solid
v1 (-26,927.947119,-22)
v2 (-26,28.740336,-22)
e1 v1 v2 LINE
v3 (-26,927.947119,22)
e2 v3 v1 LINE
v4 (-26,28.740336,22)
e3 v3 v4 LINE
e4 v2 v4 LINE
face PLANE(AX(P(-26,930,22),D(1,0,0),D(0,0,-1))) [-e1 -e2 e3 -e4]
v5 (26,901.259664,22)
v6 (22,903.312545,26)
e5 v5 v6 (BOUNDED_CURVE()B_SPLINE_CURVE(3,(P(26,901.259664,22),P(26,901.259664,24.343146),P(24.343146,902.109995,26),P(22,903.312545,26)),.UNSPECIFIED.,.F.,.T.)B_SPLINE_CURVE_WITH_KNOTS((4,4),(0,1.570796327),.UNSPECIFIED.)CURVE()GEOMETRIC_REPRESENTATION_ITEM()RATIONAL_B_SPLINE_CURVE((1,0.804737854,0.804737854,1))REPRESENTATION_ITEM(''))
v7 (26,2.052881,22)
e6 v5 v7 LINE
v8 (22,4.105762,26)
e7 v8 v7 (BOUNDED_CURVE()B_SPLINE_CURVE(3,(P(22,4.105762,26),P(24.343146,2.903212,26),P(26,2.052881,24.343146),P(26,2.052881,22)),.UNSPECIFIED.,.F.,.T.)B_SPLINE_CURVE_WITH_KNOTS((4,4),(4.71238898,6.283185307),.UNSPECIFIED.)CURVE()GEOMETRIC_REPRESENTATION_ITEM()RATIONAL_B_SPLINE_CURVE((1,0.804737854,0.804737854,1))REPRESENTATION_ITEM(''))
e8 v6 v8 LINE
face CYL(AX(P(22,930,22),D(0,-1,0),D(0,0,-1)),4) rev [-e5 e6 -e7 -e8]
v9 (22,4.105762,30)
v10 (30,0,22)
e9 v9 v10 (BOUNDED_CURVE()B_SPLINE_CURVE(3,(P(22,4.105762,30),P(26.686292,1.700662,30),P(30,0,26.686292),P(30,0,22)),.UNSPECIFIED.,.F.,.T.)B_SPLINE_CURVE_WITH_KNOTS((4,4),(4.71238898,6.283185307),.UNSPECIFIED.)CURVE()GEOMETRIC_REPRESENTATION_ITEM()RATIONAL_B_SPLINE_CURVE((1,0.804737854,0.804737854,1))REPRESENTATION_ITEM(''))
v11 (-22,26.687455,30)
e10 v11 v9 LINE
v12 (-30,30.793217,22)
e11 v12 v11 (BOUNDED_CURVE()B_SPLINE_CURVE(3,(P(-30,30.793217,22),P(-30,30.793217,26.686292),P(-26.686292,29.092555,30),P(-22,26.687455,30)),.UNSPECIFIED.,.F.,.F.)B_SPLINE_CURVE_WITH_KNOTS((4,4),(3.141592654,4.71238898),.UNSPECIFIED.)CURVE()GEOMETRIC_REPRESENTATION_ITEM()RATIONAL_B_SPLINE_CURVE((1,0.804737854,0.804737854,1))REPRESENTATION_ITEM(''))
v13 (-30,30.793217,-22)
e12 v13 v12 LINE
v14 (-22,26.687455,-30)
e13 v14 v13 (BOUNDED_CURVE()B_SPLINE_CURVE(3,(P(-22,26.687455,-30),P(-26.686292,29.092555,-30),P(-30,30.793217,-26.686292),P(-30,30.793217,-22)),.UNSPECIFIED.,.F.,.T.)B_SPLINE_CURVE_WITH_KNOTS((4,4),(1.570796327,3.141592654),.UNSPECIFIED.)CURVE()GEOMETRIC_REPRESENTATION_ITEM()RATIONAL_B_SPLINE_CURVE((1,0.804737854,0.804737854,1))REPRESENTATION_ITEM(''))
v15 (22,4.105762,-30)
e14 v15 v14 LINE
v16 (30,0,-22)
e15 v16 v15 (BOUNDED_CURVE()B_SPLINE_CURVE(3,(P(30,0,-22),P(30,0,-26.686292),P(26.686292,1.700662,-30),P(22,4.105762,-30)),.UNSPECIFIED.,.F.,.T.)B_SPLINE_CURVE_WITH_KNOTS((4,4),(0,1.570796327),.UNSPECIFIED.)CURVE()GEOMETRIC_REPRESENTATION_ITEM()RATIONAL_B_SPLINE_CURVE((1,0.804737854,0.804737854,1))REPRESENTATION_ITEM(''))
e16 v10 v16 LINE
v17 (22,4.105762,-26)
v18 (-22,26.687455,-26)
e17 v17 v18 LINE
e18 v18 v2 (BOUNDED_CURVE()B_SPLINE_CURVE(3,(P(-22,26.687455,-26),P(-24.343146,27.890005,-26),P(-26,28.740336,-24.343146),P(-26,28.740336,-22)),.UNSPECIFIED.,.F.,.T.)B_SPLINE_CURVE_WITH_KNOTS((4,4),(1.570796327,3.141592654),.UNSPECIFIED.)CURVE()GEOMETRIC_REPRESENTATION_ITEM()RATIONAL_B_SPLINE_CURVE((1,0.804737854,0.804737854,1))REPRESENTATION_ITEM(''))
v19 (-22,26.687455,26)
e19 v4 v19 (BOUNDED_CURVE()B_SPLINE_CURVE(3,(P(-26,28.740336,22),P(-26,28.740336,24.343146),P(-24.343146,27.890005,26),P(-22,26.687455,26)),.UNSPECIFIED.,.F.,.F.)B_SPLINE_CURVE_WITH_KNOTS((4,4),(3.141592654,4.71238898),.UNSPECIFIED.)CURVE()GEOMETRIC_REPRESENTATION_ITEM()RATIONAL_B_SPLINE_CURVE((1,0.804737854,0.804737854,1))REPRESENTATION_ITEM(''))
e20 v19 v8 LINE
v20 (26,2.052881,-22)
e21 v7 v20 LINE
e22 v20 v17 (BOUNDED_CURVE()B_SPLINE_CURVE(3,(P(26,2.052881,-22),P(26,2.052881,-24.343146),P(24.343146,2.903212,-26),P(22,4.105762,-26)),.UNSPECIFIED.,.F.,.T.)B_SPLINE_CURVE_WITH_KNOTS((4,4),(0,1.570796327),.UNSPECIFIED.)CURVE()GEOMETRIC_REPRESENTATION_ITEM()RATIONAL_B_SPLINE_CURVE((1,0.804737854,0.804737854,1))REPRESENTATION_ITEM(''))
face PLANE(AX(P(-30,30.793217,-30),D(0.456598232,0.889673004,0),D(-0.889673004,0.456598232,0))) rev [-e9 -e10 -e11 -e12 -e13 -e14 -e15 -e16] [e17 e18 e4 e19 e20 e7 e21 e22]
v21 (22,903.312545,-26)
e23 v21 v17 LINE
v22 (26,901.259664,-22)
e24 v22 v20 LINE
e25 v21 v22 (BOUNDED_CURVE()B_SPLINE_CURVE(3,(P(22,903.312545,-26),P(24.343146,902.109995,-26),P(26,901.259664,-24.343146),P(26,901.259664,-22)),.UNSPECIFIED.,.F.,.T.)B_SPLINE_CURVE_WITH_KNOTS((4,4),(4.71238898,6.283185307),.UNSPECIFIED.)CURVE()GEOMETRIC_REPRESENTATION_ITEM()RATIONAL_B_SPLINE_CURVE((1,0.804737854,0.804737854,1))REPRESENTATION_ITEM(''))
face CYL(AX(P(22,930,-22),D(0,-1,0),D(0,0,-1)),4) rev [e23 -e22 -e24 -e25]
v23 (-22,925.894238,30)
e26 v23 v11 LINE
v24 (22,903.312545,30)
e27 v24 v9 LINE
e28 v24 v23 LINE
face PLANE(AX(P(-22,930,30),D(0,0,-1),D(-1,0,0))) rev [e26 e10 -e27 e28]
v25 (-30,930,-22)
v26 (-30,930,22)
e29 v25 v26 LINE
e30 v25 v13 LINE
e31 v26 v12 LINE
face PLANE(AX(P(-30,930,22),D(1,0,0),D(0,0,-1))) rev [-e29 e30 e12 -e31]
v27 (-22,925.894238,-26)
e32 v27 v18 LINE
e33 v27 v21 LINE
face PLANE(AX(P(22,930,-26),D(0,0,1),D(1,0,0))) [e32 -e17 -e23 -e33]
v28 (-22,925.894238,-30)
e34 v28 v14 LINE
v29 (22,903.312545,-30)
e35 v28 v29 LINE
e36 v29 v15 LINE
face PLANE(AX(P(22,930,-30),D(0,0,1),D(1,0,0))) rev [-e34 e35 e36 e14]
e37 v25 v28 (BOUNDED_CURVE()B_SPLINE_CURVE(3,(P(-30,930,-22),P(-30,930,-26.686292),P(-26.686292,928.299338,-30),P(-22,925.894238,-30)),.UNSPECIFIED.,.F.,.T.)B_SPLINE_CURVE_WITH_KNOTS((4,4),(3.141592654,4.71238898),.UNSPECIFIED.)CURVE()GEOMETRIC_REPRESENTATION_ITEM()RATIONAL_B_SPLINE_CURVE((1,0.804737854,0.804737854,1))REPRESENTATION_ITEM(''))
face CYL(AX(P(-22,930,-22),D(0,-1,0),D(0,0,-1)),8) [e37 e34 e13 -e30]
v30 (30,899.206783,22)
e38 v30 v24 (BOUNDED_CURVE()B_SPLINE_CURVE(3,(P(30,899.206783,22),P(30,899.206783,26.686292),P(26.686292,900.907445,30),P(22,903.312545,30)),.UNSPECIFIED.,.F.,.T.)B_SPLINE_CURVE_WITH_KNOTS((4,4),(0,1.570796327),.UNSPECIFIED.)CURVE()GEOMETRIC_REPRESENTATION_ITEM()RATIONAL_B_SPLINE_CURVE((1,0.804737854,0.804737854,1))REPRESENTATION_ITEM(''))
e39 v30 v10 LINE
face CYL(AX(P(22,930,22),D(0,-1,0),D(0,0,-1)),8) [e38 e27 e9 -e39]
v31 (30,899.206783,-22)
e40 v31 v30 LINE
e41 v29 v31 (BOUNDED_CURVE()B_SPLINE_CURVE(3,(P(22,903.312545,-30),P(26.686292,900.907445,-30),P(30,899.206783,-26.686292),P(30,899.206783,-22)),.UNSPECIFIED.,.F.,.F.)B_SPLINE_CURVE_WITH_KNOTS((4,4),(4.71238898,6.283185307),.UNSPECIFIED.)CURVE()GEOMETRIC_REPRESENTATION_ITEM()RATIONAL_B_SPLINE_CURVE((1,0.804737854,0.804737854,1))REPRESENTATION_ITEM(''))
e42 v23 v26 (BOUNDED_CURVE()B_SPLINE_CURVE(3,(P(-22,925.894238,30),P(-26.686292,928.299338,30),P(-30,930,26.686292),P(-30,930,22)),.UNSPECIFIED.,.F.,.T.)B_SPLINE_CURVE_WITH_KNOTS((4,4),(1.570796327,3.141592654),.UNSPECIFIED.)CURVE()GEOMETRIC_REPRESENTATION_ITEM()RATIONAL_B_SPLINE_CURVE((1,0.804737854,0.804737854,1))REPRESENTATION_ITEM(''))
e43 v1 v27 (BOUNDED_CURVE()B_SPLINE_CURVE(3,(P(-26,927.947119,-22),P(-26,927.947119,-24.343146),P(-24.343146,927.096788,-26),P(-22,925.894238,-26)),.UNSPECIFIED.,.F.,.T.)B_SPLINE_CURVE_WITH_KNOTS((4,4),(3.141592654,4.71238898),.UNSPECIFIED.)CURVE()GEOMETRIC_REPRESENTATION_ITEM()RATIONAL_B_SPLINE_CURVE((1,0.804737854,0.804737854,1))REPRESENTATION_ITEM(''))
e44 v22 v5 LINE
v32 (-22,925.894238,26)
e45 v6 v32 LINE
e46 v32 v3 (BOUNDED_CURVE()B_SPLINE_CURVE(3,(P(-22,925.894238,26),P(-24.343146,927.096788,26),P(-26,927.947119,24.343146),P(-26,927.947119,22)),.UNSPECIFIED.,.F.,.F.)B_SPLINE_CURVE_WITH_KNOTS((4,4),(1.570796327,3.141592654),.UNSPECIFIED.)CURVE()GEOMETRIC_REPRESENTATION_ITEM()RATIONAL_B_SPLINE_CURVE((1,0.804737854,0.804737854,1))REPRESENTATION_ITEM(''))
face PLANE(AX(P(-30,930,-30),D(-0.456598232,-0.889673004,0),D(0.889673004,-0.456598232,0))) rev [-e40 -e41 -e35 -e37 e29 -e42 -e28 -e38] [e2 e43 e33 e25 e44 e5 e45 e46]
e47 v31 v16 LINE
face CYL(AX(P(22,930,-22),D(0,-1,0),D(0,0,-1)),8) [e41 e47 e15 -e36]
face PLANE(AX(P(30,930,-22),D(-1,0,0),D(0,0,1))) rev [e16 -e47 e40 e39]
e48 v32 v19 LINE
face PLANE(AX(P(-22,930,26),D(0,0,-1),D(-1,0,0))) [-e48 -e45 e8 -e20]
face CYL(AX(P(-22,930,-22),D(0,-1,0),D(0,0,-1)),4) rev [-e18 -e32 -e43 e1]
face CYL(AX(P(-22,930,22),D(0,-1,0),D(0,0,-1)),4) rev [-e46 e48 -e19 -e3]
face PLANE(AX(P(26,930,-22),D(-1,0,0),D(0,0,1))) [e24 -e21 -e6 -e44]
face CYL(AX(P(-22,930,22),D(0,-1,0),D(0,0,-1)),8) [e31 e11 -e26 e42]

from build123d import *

# Parameters (mm, degrees)
GB_T_6728_2002_SQUARE_HOLLOW_SECTION_60_DEPTH = 930
CUT_EXTRUDE1_DEPTH                            = 933.416216075
CUT_EXTRUDE1_DEPTH_BACK                       = 933.416216075


with BuildPart() as part:
    # Sketch1 → GB/T 6728-2002 square hollow section 60×60×4(1) (new body)
    with BuildSketch(Plane(origin=(0, 0, 0), x_dir=(-1, 0, 0), z_dir=(0, 1, 0))):
        with BuildLine():
            Line((-22, -30), (22, -30))
            ThreePointArc((22, -30), (27.656854249, -27.656854249), (30, -22))
            Line((30, -22), (30, 22))
            ThreePointArc((30, 22), (27.656854249, 27.656854249), (22, 30))
            Line((22, 30), (-22, 30))
            ThreePointArc((-22, 30), (-27.656854249, 27.656854249), (-30, 22))
            Line((-30, 22), (-30, -22))
            ThreePointArc((-30, -22), (-27.656854249, -27.656854249), (-22, -30))
        make_face()
        with BuildLine():
            Line((-22, -26), (22, -26))
            ThreePointArc((22, -26), (24.828427125, -24.828427125), (26, -22))
            Line((26, -22), (26, 22))
            ThreePointArc((26, 22), (24.828427125, 24.828427125), (22, 26))
            Line((22, 26), (-22, 26))
            ThreePointArc((-22, 26), (-24.828427125, 24.828427125), (-26, 22))
            Line((-26, 22), (-26, -22))
            ThreePointArc((-26, -22), (-24.828427125, -24.828427125), (-22, -26))
        make_face(mode=Mode.SUBTRACT)
    extrude(amount=GB_T_6728_2002_SQUARE_HOLLOW_SECTION_60_DEPTH)

    # Sketch2 → Cut-Extrude1 (cut, two sides: drawn at the far end of the back side and taken through both)
    with BuildSketch(Plane.XY.offset(30).offset(-CUT_EXTRUDE1_DEPTH_BACK)):
        Polygon((-30, 930), (30, 899.206782946), (30, 930), align=None)
        Polygon((-30, 0), (-30, 30.793217054), (30, 0), align=None)
    extrude(amount=CUT_EXTRUDE1_DEPTH + CUT_EXTRUDE1_DEPTH_BACK, mode=Mode.SUBTRACT)


solid = part.part
